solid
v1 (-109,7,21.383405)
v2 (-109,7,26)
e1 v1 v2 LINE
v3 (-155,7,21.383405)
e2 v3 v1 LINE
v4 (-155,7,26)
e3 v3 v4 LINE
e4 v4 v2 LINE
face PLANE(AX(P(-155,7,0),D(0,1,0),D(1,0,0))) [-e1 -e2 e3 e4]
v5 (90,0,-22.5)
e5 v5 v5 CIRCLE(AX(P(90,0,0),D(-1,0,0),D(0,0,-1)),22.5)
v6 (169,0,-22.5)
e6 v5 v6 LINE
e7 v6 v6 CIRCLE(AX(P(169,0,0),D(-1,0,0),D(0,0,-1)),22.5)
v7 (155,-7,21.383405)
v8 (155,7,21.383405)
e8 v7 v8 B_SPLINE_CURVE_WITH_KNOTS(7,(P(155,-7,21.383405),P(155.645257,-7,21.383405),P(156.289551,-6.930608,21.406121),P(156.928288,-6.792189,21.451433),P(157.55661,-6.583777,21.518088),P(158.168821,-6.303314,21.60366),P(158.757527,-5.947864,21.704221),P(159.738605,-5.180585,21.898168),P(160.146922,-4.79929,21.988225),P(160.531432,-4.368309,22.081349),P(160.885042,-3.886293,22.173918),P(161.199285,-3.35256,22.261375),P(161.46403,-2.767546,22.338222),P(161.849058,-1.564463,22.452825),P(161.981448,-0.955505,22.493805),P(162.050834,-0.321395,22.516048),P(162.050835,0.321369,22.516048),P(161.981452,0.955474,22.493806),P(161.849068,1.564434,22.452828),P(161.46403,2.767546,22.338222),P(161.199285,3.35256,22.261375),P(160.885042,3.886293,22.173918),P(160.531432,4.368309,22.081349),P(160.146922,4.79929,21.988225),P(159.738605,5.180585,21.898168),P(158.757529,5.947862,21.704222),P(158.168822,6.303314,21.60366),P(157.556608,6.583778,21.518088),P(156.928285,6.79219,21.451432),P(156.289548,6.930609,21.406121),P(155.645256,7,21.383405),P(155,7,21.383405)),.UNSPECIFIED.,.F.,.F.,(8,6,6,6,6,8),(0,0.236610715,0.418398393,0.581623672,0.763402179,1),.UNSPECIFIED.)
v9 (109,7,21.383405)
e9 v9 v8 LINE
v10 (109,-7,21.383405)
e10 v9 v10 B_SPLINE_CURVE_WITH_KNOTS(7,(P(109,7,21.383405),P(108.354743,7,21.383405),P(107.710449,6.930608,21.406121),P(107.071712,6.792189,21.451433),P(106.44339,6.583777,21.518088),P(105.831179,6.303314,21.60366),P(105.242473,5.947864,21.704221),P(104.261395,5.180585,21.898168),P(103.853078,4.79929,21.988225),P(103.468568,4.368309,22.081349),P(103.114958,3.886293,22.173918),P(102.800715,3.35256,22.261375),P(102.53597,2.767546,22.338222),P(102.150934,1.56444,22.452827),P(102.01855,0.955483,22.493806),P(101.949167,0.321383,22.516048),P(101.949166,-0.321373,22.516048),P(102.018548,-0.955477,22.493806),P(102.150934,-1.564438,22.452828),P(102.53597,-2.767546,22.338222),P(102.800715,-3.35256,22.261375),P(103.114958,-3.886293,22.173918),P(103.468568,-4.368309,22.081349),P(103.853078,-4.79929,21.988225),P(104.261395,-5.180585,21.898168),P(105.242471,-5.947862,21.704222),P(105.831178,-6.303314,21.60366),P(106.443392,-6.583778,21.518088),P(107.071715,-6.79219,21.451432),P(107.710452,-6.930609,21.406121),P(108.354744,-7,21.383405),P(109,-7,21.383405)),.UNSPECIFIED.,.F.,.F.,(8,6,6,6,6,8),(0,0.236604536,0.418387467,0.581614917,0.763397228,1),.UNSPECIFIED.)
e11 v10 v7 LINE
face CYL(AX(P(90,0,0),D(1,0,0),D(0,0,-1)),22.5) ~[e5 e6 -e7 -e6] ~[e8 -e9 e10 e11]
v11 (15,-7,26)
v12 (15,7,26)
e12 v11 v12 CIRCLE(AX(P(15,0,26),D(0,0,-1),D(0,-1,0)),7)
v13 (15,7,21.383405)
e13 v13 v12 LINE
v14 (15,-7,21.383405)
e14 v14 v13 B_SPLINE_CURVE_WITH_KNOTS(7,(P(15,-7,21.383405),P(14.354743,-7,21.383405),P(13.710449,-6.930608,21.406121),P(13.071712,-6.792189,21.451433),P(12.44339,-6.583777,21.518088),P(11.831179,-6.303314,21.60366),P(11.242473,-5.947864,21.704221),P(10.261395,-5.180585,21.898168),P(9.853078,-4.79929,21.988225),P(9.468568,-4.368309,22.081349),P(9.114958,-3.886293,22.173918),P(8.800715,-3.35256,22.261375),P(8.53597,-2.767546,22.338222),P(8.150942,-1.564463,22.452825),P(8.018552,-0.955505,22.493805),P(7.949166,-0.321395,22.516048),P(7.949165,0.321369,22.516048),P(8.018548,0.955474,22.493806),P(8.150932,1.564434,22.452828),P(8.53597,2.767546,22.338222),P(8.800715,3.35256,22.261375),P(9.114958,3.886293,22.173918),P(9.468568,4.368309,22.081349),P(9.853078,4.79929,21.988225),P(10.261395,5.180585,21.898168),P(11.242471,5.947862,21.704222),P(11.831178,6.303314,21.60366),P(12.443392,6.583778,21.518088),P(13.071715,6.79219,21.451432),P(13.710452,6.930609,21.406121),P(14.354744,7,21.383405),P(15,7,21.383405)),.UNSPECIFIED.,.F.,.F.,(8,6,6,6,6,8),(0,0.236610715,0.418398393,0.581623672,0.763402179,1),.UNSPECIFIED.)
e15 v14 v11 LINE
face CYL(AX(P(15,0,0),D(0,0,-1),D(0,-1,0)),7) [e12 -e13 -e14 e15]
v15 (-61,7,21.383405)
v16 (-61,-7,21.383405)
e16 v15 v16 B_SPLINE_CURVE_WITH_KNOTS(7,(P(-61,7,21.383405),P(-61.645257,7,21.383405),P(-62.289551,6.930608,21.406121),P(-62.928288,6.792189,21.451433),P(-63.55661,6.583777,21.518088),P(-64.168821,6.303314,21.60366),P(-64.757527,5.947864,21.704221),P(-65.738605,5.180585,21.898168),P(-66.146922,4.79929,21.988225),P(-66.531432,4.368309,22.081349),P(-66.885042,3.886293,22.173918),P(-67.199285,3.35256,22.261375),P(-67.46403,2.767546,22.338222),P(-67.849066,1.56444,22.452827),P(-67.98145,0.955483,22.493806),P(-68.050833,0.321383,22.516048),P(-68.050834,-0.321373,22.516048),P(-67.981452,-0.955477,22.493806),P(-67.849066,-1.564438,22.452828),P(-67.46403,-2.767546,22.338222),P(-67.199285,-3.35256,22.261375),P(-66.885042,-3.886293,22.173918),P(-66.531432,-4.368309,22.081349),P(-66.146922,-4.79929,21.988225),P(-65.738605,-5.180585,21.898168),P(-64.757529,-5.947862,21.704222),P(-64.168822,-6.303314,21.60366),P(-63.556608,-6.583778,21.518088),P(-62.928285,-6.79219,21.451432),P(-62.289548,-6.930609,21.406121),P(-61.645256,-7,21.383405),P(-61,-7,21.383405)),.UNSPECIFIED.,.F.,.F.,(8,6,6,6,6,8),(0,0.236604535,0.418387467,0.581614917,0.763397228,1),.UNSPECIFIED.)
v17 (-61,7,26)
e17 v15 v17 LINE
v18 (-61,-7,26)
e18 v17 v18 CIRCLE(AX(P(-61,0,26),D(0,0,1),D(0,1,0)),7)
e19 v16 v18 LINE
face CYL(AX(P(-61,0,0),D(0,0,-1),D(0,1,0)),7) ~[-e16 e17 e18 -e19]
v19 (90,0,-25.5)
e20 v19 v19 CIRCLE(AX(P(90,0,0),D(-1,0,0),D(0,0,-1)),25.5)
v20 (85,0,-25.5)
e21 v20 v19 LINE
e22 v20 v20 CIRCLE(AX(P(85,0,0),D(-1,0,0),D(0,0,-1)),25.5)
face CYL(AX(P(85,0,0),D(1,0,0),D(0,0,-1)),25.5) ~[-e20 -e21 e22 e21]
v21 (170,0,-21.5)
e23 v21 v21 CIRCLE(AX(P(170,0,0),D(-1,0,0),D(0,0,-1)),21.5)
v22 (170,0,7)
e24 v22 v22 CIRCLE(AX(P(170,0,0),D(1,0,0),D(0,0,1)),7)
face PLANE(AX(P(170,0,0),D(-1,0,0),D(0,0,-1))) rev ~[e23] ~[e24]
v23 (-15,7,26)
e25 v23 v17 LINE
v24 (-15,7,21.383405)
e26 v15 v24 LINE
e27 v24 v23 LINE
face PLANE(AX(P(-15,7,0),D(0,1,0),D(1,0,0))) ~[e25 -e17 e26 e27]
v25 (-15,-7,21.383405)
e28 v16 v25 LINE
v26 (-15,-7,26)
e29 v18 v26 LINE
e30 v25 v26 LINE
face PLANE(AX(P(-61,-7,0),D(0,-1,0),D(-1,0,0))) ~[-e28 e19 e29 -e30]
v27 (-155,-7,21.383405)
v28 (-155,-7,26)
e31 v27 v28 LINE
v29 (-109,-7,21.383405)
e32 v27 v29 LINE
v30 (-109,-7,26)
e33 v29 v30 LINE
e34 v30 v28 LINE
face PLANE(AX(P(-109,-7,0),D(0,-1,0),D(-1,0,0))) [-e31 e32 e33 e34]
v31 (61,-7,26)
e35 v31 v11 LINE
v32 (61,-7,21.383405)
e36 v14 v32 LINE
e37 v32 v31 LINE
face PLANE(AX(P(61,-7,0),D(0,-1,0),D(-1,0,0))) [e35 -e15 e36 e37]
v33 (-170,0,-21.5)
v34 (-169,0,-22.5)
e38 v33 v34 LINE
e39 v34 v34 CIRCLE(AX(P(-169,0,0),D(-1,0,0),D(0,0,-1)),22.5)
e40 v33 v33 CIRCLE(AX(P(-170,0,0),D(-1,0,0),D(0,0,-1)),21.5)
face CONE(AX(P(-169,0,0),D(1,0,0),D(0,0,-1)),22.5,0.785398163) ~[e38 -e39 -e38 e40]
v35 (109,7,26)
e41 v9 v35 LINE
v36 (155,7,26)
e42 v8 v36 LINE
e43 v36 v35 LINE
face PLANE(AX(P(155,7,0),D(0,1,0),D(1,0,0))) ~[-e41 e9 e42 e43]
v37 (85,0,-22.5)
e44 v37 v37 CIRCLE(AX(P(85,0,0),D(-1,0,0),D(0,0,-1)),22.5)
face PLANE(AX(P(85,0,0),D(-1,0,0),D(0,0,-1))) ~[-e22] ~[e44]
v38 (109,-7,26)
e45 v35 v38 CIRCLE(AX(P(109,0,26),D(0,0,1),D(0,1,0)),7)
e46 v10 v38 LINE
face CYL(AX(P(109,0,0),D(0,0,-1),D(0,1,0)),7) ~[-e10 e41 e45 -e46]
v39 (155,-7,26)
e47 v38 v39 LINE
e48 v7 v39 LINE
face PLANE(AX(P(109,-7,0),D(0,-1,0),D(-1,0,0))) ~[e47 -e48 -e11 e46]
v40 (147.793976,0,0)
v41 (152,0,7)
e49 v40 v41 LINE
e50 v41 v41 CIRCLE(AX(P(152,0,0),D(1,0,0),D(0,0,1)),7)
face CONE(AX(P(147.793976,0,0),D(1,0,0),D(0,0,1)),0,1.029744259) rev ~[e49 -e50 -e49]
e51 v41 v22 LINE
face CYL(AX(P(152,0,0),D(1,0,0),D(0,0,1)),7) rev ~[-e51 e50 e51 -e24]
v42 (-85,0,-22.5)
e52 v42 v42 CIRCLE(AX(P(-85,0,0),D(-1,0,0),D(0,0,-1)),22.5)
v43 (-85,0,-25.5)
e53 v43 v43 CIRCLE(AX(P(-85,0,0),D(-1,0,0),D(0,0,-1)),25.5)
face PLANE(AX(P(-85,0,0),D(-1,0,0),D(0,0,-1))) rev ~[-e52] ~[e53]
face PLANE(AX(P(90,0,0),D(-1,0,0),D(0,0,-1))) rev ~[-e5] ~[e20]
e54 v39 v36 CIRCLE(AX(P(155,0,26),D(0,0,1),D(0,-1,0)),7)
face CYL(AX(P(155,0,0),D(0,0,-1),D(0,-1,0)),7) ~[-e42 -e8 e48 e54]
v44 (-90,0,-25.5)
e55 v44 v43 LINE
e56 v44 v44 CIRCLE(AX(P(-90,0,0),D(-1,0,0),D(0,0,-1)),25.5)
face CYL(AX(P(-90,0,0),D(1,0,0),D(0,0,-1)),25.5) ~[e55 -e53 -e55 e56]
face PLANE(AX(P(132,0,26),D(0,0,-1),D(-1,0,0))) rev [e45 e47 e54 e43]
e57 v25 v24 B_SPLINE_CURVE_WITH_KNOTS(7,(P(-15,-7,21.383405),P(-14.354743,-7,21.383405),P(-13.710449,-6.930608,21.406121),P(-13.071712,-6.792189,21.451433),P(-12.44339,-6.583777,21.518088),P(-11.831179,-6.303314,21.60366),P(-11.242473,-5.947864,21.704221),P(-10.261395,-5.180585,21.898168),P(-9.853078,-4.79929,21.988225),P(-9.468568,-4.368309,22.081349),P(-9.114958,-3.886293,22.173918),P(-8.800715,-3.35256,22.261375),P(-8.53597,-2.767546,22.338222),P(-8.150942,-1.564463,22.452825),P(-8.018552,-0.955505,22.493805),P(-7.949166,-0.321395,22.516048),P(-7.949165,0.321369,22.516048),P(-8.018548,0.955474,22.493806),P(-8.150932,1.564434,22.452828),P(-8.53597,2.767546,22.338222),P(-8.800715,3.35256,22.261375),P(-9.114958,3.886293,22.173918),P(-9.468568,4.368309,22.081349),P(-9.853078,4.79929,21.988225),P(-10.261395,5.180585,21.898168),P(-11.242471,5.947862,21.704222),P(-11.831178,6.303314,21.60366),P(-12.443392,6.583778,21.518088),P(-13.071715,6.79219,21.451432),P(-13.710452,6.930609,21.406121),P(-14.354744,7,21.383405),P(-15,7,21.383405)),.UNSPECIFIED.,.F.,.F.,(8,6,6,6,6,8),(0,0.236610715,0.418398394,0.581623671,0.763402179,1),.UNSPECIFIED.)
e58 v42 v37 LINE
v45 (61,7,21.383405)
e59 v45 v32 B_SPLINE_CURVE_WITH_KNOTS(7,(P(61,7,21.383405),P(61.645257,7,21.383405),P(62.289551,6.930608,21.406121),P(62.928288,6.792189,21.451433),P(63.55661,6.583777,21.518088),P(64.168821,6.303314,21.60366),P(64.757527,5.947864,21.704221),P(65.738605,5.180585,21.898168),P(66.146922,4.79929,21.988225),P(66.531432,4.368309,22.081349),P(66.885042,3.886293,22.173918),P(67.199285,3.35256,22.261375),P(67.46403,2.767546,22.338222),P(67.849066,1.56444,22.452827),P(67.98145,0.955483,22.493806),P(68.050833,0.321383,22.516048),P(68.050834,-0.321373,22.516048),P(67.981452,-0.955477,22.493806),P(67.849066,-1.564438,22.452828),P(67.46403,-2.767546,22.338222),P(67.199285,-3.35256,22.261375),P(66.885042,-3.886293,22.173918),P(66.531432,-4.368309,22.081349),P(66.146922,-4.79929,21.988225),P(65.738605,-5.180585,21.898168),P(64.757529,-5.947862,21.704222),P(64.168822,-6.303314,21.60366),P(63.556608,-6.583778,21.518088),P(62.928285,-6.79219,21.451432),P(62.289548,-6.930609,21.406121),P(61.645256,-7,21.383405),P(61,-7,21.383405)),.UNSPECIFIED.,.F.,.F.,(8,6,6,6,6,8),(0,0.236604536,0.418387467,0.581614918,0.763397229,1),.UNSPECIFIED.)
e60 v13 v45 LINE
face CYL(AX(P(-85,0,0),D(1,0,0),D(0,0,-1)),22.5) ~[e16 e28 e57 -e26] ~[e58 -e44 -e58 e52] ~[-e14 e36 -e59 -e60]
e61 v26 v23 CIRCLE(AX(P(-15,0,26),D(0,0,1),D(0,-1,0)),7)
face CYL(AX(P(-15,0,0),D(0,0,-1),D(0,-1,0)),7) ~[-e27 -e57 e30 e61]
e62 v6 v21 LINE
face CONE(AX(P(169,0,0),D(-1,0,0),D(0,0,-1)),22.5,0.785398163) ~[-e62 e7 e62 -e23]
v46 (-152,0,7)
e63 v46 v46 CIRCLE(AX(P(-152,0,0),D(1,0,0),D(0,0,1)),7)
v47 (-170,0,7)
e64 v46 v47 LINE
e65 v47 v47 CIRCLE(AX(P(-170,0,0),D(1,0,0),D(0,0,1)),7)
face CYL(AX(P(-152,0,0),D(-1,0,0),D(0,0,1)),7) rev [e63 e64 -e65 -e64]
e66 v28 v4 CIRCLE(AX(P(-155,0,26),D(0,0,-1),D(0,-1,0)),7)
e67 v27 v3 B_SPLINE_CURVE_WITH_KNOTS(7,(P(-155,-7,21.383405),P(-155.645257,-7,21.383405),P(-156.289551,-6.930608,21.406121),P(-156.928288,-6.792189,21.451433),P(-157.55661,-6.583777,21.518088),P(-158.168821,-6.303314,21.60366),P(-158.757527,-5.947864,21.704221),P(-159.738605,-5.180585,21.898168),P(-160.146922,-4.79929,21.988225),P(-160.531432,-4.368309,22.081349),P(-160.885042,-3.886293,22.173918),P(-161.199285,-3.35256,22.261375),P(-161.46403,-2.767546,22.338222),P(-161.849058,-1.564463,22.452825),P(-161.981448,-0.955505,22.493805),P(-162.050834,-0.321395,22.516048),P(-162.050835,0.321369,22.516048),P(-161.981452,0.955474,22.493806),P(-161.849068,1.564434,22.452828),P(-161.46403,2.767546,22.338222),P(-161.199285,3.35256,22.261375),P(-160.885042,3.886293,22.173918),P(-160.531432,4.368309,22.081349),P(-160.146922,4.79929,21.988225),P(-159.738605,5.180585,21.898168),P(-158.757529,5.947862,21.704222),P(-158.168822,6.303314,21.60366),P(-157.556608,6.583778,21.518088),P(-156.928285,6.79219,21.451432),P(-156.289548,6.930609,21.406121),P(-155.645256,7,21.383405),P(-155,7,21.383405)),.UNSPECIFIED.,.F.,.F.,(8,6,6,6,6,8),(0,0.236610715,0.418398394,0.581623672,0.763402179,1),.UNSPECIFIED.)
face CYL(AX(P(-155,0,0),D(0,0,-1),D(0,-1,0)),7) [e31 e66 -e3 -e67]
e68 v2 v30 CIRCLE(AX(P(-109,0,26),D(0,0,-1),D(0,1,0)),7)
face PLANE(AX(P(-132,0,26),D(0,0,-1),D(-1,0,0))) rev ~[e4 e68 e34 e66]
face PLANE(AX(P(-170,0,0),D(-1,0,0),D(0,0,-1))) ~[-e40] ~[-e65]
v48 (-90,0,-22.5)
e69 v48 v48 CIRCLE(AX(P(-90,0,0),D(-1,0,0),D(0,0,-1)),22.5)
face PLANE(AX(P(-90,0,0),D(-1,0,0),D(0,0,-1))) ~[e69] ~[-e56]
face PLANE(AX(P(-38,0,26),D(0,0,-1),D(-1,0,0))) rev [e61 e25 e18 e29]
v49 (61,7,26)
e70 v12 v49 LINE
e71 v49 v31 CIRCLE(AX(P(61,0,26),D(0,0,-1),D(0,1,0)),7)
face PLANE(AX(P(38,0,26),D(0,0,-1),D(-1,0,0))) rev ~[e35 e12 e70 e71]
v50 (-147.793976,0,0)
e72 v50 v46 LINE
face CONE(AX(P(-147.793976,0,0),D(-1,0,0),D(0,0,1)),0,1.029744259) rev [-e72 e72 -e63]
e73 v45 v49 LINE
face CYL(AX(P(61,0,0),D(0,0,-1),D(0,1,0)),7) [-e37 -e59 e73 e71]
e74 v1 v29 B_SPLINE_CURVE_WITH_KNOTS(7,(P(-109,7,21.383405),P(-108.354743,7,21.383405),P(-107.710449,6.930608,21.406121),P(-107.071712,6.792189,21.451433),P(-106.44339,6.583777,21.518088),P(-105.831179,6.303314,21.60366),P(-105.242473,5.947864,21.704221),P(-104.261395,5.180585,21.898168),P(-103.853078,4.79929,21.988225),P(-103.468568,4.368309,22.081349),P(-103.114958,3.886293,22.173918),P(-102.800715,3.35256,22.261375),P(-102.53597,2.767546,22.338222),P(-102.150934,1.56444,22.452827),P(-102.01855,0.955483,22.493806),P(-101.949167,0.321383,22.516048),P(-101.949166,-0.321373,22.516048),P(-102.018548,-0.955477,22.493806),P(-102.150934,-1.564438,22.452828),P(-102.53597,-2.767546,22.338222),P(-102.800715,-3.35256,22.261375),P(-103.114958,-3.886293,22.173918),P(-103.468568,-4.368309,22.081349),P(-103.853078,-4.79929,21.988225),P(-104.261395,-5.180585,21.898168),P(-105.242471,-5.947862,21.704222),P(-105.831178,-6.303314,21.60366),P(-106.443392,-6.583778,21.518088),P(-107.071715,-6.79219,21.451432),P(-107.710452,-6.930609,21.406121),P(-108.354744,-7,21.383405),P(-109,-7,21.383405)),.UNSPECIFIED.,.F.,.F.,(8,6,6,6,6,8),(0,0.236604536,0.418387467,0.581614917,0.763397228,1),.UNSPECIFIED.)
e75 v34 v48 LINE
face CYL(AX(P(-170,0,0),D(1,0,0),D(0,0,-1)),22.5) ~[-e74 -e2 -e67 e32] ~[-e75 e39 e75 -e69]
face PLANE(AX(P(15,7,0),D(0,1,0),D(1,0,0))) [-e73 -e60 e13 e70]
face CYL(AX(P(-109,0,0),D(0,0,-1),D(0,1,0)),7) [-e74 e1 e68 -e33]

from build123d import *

# Parameters (mm, degrees)
CHAMFER1_SIZE        = 1
BOSS_EXTRUDE1_DEPTH  = 26
MIRROR6_COPY_1_DEPTH = 26


with BuildPart() as part:
    # Sketch1 → Revolve1 (revolve)
    with BuildSketch(Plane.XY, mode=Mode.PRIVATE) as revolve1_sk:
        Polygon((170, 0), (-170, 0), (-170, 22.5), (-90, 22.5), (-90, 25.5), (-85, 25.5), (-85, 22.5), (85, 22.5), (85, 25.5), (90, 25.5), (90, 22.5), (170, 22.5), align=None)
    revolve(revolve1_sk.sketch.rotate(Axis((170, 0, 0), (-1, 0, 0)), 90), axis=Axis((170, 0, 0), (-1, 0, 0)))

    # Chamfer1
    chamfer1_edges = [part.edges().sort_by_distance(p)[0] for p in [
        (-170, 0, 22.5),
        (170, 0, 22.5),
    ]]
    chamfer(chamfer1_edges, length=CHAMFER1_SIZE)

    # Sketch2 → Boss-Extrude1 (add)
    with BuildSketch(Plane.XY):
        with BuildLine():
            Line((-155, 7), (-109, 7))
            ThreePointArc((-109, 7), (-102, 0), (-109, -7))
            Line((-109, -7), (-155, -7))
            ThreePointArc((-155, -7), (-162, 0), (-155, 7))
        make_face()
    boss_extrude1 = extrude(amount=BOSS_EXTRUDE1_DEPTH)

    # Mirror1: Boss-Extrude1 across plane
    add(boss_extrude1.mirror(Plane(origin=(0, 0, 0), x_dir=(0, 0, 1), z_dir=(1, 0, 0))))

    # Sketch3 → M16 Tapped Hole1 (revolve, cut)
    with BuildSketch(Plane(origin=(-170, 0, 0), x_dir=(0, 0, 1), z_dir=(0, 1, 0))):
        Polygon((0, 0), (0, 22.206024333), (7, 18), (7, 0), align=None)
    m16_tapped_hole1 = revolve(axis=Axis((-176.35, 0, 0), (1, 0, 0)), mode=Mode.SUBTRACT)

    # Mirror2: M16 Tapped Hole1 across plane
    add(m16_tapped_hole1.mirror(Plane(origin=(0, 0, 0), x_dir=(0, 0, 1), z_dir=(1, 0, 0))), mode=Mode.SUBTRACT)

    # Mirror3: Boss-Extrude1 across plane
    add(boss_extrude1.mirror(Plane(origin=(-85, 25.5, 0), x_dir=(0, 0, 1), z_dir=(1, 0, 0))))

    # Mirror6 copy 1 sketch → Mirror6 copy 1 (add)
    with BuildSketch(Plane(origin=(170, 0, 0), x_dir=(1, 0, 0), z_dir=(0, 0, 1))):
        with BuildLine():
            Line((-155, 7), (-109, 7))
            ThreePointArc((-109, 7), (-102, 0), (-109, -7))
            Line((-109, -7), (-155, -7))
            ThreePointArc((-155, -7), (-162, 0), (-155, 7))
        make_face()
    extrude(amount=MIRROR6_COPY_1_DEPTH)


solid = part.part
